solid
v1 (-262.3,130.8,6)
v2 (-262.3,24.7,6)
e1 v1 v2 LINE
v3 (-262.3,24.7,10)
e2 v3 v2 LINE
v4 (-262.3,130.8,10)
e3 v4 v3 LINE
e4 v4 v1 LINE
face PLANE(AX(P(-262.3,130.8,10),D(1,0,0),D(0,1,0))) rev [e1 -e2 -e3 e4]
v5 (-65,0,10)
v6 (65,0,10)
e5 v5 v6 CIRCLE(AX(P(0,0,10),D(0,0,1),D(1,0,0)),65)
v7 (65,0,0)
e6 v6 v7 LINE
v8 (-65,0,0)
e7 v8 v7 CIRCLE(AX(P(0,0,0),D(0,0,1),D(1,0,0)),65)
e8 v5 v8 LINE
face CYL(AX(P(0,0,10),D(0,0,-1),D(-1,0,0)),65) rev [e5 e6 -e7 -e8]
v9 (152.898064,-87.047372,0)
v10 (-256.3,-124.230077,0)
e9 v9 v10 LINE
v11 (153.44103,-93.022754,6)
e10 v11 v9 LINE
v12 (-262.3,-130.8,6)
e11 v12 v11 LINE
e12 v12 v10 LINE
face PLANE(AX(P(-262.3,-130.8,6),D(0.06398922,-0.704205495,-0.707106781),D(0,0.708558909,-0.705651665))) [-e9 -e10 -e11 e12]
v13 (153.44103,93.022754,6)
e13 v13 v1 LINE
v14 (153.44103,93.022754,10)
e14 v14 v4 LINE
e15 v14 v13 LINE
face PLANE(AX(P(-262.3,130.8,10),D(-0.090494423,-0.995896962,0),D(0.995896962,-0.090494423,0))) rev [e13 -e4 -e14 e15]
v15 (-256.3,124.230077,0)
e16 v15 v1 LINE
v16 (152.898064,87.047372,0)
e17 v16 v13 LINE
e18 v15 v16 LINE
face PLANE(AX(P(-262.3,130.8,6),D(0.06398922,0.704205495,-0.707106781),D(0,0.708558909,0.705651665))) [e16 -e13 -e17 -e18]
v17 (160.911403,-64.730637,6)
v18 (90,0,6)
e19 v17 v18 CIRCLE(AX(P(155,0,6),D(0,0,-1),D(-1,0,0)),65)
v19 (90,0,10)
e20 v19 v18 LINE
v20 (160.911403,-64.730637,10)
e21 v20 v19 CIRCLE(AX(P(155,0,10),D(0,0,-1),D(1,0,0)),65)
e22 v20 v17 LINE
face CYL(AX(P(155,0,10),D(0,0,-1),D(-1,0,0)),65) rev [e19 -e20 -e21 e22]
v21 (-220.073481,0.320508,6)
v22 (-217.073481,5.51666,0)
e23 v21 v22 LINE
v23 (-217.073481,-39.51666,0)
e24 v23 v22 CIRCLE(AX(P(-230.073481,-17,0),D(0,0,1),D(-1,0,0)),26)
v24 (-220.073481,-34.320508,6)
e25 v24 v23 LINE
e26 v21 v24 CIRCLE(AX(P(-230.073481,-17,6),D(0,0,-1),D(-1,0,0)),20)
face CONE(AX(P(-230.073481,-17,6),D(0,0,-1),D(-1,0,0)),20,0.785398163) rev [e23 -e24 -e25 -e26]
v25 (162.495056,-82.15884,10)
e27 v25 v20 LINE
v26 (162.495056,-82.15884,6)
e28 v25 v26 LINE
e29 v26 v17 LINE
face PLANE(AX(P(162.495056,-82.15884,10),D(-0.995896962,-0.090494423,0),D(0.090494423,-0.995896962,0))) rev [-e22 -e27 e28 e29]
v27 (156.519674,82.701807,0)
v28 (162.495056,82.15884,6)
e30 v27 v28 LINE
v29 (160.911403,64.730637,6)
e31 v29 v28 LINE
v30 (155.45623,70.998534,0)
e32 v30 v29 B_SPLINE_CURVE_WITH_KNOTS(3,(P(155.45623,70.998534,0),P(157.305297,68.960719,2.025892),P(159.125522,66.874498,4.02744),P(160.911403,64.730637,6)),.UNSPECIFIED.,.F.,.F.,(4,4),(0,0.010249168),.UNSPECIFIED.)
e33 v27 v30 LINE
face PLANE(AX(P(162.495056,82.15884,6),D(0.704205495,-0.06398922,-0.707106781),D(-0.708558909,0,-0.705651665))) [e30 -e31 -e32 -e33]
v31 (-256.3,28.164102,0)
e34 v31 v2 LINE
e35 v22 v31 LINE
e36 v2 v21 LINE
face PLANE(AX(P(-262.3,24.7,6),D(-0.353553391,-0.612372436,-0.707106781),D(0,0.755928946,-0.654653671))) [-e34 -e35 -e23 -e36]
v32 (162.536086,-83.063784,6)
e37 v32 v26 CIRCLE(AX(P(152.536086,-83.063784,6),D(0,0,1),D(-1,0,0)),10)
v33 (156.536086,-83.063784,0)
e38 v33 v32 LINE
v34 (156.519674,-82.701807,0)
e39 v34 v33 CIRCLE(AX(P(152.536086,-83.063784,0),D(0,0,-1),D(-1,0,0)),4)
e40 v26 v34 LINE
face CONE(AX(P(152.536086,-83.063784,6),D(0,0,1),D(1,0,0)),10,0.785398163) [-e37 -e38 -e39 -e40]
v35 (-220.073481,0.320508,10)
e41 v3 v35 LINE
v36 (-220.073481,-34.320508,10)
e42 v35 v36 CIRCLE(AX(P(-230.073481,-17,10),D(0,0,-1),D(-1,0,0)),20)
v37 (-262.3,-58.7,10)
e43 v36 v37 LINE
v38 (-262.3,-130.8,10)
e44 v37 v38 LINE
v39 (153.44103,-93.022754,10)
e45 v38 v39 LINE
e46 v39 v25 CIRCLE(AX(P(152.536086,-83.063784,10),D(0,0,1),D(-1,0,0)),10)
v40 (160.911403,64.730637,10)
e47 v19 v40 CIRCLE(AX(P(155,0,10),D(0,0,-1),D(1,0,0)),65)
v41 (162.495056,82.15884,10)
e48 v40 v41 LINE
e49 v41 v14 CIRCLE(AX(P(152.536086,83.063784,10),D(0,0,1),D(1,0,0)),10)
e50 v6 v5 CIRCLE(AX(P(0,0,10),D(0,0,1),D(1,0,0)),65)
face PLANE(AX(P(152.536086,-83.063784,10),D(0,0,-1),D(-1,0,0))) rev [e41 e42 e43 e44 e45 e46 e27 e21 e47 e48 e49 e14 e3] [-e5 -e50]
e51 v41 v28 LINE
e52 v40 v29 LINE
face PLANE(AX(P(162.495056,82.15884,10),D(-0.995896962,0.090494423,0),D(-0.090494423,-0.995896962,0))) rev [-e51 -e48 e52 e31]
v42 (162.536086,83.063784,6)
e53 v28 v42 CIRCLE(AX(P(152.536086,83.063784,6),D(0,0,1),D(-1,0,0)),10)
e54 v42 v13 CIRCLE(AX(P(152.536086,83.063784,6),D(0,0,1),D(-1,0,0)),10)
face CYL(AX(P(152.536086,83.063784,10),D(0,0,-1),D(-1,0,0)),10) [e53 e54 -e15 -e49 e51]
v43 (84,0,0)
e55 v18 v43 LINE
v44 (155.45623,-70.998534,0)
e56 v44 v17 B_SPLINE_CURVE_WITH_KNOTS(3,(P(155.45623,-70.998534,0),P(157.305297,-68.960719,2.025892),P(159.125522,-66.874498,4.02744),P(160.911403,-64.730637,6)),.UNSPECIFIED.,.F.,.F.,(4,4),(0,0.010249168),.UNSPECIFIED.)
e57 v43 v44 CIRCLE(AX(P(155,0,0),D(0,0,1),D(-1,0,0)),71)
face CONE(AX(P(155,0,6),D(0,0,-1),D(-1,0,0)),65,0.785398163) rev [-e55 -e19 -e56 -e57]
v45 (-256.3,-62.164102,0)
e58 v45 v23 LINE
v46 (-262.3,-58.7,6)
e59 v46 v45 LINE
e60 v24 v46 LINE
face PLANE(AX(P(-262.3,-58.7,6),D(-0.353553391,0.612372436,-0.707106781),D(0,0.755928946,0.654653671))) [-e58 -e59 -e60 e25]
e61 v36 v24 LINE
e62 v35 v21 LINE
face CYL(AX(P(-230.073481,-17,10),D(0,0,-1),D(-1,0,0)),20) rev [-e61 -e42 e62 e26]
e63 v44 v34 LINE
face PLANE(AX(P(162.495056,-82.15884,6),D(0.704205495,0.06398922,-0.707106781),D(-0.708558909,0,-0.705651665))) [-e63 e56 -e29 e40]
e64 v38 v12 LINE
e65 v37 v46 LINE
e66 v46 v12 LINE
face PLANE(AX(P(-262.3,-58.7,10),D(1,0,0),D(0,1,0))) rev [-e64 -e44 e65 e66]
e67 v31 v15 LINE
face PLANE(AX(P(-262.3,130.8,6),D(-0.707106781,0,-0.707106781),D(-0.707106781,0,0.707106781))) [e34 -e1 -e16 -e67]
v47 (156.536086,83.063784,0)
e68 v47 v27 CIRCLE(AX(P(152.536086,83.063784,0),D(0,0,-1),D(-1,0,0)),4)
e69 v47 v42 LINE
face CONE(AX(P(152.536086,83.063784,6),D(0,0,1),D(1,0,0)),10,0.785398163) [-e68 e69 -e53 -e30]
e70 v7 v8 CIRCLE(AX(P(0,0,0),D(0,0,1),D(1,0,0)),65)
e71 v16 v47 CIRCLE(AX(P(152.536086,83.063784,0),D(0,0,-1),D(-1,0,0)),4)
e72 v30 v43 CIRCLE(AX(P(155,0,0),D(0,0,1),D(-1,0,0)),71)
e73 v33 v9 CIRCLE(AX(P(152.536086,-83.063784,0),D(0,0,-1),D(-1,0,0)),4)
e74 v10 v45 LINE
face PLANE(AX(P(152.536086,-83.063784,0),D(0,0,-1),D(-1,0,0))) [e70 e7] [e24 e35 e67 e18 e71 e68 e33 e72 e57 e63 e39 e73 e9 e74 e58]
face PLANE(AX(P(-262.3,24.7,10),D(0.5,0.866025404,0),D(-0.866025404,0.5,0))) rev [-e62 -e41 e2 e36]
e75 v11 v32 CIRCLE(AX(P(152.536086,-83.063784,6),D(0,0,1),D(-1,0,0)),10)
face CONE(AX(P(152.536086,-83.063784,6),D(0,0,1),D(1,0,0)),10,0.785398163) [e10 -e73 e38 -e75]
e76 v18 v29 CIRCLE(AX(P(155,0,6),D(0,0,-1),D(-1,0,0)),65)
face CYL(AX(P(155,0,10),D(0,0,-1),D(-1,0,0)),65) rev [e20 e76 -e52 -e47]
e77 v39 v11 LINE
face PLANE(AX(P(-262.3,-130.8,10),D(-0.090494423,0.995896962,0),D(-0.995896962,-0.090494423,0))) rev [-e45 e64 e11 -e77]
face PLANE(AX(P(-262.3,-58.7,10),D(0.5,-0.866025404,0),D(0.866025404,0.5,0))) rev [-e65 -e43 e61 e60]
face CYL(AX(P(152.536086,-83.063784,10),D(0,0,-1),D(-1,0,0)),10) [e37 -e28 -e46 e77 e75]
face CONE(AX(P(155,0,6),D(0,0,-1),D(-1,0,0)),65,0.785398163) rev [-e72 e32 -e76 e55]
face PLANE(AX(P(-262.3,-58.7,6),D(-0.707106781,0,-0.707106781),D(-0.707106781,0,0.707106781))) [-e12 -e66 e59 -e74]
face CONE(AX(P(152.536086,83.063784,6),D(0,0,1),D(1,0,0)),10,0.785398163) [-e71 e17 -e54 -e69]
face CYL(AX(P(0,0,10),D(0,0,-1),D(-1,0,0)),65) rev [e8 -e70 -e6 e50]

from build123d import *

# Parameters (mm, degrees)
SKETCH1_R           = 65
BOSS_EXTRUDE1_DEPTH = 10
CHAMFER1_SIZE       = 6


with BuildPart() as part:
    # Sketch1 → Boss-Extrude1 (new body)
    with BuildSketch(Plane.XY):
        with BuildLine():
            Line((-262.3, 130.8), (-262.3, 24.7))
            Line((-262.3, 24.7), (-220.073481324, 0.320508076))
            ThreePointArc((-220.073481324, 0.320508076), (-210.073481324, -17), (-220.073481324, -34.320508076))
            Line((-220.073481324, -34.320508076), (-262.3, -58.7))
            Line((-262.3, -58.7), (-262.3, -130.8))
            Line((-262.3, -130.8), (153.441030377, -93.022753927))
            ThreePointArc((153.441030377, -93.022753927), (160.218033303, -89.465947057), (162.495055771, -82.158840075))
            Line((162.495055771, -82.158840075), (160.91140277, -64.73063662))
            ThreePointArc((160.91140277, -64.73063662), (90, 0), (160.91140277, 64.73063662))
            Line((160.91140277, 64.73063662), (162.495055771, 82.158840075))
            ThreePointArc((162.495055771, 82.158840075), (160.218033303, 89.465947057), (153.441030377, 93.022753927))
            Line((153.441030377, 93.022753927), (-262.3, 130.8))
        make_face()
        Circle(SKETCH1_R, mode=Mode.SUBTRACT)
    extrude(amount=BOSS_EXTRUDE1_DEPTH)

    # Chamfer1
    chamfer1_edges = [part.edges().sort_by_distance(p)[0] for p in [
        (-241.186740662, -46.510254038, 0),
        (-210.073481324, -17, 0),
        (-241.186740662, 12.510254038, 0),
        (-262.3, 77.75, 0),
        (-54.429484811, 111.911376963, 0),
        (160.218033303, 89.465947057, 0),
        (161.703229271, 73.444738348, 0),
        (90, 0, 0),
        (161.703229271, -73.444738348, 0),
        (160.218033303, -89.465947057, 0),
        (-54.429484811, -111.911376963, 0),
        (-262.3, -94.75, 0),
    ]]
    chamfer(chamfer1_edges, length=CHAMFER1_SIZE)


solid = part.part
